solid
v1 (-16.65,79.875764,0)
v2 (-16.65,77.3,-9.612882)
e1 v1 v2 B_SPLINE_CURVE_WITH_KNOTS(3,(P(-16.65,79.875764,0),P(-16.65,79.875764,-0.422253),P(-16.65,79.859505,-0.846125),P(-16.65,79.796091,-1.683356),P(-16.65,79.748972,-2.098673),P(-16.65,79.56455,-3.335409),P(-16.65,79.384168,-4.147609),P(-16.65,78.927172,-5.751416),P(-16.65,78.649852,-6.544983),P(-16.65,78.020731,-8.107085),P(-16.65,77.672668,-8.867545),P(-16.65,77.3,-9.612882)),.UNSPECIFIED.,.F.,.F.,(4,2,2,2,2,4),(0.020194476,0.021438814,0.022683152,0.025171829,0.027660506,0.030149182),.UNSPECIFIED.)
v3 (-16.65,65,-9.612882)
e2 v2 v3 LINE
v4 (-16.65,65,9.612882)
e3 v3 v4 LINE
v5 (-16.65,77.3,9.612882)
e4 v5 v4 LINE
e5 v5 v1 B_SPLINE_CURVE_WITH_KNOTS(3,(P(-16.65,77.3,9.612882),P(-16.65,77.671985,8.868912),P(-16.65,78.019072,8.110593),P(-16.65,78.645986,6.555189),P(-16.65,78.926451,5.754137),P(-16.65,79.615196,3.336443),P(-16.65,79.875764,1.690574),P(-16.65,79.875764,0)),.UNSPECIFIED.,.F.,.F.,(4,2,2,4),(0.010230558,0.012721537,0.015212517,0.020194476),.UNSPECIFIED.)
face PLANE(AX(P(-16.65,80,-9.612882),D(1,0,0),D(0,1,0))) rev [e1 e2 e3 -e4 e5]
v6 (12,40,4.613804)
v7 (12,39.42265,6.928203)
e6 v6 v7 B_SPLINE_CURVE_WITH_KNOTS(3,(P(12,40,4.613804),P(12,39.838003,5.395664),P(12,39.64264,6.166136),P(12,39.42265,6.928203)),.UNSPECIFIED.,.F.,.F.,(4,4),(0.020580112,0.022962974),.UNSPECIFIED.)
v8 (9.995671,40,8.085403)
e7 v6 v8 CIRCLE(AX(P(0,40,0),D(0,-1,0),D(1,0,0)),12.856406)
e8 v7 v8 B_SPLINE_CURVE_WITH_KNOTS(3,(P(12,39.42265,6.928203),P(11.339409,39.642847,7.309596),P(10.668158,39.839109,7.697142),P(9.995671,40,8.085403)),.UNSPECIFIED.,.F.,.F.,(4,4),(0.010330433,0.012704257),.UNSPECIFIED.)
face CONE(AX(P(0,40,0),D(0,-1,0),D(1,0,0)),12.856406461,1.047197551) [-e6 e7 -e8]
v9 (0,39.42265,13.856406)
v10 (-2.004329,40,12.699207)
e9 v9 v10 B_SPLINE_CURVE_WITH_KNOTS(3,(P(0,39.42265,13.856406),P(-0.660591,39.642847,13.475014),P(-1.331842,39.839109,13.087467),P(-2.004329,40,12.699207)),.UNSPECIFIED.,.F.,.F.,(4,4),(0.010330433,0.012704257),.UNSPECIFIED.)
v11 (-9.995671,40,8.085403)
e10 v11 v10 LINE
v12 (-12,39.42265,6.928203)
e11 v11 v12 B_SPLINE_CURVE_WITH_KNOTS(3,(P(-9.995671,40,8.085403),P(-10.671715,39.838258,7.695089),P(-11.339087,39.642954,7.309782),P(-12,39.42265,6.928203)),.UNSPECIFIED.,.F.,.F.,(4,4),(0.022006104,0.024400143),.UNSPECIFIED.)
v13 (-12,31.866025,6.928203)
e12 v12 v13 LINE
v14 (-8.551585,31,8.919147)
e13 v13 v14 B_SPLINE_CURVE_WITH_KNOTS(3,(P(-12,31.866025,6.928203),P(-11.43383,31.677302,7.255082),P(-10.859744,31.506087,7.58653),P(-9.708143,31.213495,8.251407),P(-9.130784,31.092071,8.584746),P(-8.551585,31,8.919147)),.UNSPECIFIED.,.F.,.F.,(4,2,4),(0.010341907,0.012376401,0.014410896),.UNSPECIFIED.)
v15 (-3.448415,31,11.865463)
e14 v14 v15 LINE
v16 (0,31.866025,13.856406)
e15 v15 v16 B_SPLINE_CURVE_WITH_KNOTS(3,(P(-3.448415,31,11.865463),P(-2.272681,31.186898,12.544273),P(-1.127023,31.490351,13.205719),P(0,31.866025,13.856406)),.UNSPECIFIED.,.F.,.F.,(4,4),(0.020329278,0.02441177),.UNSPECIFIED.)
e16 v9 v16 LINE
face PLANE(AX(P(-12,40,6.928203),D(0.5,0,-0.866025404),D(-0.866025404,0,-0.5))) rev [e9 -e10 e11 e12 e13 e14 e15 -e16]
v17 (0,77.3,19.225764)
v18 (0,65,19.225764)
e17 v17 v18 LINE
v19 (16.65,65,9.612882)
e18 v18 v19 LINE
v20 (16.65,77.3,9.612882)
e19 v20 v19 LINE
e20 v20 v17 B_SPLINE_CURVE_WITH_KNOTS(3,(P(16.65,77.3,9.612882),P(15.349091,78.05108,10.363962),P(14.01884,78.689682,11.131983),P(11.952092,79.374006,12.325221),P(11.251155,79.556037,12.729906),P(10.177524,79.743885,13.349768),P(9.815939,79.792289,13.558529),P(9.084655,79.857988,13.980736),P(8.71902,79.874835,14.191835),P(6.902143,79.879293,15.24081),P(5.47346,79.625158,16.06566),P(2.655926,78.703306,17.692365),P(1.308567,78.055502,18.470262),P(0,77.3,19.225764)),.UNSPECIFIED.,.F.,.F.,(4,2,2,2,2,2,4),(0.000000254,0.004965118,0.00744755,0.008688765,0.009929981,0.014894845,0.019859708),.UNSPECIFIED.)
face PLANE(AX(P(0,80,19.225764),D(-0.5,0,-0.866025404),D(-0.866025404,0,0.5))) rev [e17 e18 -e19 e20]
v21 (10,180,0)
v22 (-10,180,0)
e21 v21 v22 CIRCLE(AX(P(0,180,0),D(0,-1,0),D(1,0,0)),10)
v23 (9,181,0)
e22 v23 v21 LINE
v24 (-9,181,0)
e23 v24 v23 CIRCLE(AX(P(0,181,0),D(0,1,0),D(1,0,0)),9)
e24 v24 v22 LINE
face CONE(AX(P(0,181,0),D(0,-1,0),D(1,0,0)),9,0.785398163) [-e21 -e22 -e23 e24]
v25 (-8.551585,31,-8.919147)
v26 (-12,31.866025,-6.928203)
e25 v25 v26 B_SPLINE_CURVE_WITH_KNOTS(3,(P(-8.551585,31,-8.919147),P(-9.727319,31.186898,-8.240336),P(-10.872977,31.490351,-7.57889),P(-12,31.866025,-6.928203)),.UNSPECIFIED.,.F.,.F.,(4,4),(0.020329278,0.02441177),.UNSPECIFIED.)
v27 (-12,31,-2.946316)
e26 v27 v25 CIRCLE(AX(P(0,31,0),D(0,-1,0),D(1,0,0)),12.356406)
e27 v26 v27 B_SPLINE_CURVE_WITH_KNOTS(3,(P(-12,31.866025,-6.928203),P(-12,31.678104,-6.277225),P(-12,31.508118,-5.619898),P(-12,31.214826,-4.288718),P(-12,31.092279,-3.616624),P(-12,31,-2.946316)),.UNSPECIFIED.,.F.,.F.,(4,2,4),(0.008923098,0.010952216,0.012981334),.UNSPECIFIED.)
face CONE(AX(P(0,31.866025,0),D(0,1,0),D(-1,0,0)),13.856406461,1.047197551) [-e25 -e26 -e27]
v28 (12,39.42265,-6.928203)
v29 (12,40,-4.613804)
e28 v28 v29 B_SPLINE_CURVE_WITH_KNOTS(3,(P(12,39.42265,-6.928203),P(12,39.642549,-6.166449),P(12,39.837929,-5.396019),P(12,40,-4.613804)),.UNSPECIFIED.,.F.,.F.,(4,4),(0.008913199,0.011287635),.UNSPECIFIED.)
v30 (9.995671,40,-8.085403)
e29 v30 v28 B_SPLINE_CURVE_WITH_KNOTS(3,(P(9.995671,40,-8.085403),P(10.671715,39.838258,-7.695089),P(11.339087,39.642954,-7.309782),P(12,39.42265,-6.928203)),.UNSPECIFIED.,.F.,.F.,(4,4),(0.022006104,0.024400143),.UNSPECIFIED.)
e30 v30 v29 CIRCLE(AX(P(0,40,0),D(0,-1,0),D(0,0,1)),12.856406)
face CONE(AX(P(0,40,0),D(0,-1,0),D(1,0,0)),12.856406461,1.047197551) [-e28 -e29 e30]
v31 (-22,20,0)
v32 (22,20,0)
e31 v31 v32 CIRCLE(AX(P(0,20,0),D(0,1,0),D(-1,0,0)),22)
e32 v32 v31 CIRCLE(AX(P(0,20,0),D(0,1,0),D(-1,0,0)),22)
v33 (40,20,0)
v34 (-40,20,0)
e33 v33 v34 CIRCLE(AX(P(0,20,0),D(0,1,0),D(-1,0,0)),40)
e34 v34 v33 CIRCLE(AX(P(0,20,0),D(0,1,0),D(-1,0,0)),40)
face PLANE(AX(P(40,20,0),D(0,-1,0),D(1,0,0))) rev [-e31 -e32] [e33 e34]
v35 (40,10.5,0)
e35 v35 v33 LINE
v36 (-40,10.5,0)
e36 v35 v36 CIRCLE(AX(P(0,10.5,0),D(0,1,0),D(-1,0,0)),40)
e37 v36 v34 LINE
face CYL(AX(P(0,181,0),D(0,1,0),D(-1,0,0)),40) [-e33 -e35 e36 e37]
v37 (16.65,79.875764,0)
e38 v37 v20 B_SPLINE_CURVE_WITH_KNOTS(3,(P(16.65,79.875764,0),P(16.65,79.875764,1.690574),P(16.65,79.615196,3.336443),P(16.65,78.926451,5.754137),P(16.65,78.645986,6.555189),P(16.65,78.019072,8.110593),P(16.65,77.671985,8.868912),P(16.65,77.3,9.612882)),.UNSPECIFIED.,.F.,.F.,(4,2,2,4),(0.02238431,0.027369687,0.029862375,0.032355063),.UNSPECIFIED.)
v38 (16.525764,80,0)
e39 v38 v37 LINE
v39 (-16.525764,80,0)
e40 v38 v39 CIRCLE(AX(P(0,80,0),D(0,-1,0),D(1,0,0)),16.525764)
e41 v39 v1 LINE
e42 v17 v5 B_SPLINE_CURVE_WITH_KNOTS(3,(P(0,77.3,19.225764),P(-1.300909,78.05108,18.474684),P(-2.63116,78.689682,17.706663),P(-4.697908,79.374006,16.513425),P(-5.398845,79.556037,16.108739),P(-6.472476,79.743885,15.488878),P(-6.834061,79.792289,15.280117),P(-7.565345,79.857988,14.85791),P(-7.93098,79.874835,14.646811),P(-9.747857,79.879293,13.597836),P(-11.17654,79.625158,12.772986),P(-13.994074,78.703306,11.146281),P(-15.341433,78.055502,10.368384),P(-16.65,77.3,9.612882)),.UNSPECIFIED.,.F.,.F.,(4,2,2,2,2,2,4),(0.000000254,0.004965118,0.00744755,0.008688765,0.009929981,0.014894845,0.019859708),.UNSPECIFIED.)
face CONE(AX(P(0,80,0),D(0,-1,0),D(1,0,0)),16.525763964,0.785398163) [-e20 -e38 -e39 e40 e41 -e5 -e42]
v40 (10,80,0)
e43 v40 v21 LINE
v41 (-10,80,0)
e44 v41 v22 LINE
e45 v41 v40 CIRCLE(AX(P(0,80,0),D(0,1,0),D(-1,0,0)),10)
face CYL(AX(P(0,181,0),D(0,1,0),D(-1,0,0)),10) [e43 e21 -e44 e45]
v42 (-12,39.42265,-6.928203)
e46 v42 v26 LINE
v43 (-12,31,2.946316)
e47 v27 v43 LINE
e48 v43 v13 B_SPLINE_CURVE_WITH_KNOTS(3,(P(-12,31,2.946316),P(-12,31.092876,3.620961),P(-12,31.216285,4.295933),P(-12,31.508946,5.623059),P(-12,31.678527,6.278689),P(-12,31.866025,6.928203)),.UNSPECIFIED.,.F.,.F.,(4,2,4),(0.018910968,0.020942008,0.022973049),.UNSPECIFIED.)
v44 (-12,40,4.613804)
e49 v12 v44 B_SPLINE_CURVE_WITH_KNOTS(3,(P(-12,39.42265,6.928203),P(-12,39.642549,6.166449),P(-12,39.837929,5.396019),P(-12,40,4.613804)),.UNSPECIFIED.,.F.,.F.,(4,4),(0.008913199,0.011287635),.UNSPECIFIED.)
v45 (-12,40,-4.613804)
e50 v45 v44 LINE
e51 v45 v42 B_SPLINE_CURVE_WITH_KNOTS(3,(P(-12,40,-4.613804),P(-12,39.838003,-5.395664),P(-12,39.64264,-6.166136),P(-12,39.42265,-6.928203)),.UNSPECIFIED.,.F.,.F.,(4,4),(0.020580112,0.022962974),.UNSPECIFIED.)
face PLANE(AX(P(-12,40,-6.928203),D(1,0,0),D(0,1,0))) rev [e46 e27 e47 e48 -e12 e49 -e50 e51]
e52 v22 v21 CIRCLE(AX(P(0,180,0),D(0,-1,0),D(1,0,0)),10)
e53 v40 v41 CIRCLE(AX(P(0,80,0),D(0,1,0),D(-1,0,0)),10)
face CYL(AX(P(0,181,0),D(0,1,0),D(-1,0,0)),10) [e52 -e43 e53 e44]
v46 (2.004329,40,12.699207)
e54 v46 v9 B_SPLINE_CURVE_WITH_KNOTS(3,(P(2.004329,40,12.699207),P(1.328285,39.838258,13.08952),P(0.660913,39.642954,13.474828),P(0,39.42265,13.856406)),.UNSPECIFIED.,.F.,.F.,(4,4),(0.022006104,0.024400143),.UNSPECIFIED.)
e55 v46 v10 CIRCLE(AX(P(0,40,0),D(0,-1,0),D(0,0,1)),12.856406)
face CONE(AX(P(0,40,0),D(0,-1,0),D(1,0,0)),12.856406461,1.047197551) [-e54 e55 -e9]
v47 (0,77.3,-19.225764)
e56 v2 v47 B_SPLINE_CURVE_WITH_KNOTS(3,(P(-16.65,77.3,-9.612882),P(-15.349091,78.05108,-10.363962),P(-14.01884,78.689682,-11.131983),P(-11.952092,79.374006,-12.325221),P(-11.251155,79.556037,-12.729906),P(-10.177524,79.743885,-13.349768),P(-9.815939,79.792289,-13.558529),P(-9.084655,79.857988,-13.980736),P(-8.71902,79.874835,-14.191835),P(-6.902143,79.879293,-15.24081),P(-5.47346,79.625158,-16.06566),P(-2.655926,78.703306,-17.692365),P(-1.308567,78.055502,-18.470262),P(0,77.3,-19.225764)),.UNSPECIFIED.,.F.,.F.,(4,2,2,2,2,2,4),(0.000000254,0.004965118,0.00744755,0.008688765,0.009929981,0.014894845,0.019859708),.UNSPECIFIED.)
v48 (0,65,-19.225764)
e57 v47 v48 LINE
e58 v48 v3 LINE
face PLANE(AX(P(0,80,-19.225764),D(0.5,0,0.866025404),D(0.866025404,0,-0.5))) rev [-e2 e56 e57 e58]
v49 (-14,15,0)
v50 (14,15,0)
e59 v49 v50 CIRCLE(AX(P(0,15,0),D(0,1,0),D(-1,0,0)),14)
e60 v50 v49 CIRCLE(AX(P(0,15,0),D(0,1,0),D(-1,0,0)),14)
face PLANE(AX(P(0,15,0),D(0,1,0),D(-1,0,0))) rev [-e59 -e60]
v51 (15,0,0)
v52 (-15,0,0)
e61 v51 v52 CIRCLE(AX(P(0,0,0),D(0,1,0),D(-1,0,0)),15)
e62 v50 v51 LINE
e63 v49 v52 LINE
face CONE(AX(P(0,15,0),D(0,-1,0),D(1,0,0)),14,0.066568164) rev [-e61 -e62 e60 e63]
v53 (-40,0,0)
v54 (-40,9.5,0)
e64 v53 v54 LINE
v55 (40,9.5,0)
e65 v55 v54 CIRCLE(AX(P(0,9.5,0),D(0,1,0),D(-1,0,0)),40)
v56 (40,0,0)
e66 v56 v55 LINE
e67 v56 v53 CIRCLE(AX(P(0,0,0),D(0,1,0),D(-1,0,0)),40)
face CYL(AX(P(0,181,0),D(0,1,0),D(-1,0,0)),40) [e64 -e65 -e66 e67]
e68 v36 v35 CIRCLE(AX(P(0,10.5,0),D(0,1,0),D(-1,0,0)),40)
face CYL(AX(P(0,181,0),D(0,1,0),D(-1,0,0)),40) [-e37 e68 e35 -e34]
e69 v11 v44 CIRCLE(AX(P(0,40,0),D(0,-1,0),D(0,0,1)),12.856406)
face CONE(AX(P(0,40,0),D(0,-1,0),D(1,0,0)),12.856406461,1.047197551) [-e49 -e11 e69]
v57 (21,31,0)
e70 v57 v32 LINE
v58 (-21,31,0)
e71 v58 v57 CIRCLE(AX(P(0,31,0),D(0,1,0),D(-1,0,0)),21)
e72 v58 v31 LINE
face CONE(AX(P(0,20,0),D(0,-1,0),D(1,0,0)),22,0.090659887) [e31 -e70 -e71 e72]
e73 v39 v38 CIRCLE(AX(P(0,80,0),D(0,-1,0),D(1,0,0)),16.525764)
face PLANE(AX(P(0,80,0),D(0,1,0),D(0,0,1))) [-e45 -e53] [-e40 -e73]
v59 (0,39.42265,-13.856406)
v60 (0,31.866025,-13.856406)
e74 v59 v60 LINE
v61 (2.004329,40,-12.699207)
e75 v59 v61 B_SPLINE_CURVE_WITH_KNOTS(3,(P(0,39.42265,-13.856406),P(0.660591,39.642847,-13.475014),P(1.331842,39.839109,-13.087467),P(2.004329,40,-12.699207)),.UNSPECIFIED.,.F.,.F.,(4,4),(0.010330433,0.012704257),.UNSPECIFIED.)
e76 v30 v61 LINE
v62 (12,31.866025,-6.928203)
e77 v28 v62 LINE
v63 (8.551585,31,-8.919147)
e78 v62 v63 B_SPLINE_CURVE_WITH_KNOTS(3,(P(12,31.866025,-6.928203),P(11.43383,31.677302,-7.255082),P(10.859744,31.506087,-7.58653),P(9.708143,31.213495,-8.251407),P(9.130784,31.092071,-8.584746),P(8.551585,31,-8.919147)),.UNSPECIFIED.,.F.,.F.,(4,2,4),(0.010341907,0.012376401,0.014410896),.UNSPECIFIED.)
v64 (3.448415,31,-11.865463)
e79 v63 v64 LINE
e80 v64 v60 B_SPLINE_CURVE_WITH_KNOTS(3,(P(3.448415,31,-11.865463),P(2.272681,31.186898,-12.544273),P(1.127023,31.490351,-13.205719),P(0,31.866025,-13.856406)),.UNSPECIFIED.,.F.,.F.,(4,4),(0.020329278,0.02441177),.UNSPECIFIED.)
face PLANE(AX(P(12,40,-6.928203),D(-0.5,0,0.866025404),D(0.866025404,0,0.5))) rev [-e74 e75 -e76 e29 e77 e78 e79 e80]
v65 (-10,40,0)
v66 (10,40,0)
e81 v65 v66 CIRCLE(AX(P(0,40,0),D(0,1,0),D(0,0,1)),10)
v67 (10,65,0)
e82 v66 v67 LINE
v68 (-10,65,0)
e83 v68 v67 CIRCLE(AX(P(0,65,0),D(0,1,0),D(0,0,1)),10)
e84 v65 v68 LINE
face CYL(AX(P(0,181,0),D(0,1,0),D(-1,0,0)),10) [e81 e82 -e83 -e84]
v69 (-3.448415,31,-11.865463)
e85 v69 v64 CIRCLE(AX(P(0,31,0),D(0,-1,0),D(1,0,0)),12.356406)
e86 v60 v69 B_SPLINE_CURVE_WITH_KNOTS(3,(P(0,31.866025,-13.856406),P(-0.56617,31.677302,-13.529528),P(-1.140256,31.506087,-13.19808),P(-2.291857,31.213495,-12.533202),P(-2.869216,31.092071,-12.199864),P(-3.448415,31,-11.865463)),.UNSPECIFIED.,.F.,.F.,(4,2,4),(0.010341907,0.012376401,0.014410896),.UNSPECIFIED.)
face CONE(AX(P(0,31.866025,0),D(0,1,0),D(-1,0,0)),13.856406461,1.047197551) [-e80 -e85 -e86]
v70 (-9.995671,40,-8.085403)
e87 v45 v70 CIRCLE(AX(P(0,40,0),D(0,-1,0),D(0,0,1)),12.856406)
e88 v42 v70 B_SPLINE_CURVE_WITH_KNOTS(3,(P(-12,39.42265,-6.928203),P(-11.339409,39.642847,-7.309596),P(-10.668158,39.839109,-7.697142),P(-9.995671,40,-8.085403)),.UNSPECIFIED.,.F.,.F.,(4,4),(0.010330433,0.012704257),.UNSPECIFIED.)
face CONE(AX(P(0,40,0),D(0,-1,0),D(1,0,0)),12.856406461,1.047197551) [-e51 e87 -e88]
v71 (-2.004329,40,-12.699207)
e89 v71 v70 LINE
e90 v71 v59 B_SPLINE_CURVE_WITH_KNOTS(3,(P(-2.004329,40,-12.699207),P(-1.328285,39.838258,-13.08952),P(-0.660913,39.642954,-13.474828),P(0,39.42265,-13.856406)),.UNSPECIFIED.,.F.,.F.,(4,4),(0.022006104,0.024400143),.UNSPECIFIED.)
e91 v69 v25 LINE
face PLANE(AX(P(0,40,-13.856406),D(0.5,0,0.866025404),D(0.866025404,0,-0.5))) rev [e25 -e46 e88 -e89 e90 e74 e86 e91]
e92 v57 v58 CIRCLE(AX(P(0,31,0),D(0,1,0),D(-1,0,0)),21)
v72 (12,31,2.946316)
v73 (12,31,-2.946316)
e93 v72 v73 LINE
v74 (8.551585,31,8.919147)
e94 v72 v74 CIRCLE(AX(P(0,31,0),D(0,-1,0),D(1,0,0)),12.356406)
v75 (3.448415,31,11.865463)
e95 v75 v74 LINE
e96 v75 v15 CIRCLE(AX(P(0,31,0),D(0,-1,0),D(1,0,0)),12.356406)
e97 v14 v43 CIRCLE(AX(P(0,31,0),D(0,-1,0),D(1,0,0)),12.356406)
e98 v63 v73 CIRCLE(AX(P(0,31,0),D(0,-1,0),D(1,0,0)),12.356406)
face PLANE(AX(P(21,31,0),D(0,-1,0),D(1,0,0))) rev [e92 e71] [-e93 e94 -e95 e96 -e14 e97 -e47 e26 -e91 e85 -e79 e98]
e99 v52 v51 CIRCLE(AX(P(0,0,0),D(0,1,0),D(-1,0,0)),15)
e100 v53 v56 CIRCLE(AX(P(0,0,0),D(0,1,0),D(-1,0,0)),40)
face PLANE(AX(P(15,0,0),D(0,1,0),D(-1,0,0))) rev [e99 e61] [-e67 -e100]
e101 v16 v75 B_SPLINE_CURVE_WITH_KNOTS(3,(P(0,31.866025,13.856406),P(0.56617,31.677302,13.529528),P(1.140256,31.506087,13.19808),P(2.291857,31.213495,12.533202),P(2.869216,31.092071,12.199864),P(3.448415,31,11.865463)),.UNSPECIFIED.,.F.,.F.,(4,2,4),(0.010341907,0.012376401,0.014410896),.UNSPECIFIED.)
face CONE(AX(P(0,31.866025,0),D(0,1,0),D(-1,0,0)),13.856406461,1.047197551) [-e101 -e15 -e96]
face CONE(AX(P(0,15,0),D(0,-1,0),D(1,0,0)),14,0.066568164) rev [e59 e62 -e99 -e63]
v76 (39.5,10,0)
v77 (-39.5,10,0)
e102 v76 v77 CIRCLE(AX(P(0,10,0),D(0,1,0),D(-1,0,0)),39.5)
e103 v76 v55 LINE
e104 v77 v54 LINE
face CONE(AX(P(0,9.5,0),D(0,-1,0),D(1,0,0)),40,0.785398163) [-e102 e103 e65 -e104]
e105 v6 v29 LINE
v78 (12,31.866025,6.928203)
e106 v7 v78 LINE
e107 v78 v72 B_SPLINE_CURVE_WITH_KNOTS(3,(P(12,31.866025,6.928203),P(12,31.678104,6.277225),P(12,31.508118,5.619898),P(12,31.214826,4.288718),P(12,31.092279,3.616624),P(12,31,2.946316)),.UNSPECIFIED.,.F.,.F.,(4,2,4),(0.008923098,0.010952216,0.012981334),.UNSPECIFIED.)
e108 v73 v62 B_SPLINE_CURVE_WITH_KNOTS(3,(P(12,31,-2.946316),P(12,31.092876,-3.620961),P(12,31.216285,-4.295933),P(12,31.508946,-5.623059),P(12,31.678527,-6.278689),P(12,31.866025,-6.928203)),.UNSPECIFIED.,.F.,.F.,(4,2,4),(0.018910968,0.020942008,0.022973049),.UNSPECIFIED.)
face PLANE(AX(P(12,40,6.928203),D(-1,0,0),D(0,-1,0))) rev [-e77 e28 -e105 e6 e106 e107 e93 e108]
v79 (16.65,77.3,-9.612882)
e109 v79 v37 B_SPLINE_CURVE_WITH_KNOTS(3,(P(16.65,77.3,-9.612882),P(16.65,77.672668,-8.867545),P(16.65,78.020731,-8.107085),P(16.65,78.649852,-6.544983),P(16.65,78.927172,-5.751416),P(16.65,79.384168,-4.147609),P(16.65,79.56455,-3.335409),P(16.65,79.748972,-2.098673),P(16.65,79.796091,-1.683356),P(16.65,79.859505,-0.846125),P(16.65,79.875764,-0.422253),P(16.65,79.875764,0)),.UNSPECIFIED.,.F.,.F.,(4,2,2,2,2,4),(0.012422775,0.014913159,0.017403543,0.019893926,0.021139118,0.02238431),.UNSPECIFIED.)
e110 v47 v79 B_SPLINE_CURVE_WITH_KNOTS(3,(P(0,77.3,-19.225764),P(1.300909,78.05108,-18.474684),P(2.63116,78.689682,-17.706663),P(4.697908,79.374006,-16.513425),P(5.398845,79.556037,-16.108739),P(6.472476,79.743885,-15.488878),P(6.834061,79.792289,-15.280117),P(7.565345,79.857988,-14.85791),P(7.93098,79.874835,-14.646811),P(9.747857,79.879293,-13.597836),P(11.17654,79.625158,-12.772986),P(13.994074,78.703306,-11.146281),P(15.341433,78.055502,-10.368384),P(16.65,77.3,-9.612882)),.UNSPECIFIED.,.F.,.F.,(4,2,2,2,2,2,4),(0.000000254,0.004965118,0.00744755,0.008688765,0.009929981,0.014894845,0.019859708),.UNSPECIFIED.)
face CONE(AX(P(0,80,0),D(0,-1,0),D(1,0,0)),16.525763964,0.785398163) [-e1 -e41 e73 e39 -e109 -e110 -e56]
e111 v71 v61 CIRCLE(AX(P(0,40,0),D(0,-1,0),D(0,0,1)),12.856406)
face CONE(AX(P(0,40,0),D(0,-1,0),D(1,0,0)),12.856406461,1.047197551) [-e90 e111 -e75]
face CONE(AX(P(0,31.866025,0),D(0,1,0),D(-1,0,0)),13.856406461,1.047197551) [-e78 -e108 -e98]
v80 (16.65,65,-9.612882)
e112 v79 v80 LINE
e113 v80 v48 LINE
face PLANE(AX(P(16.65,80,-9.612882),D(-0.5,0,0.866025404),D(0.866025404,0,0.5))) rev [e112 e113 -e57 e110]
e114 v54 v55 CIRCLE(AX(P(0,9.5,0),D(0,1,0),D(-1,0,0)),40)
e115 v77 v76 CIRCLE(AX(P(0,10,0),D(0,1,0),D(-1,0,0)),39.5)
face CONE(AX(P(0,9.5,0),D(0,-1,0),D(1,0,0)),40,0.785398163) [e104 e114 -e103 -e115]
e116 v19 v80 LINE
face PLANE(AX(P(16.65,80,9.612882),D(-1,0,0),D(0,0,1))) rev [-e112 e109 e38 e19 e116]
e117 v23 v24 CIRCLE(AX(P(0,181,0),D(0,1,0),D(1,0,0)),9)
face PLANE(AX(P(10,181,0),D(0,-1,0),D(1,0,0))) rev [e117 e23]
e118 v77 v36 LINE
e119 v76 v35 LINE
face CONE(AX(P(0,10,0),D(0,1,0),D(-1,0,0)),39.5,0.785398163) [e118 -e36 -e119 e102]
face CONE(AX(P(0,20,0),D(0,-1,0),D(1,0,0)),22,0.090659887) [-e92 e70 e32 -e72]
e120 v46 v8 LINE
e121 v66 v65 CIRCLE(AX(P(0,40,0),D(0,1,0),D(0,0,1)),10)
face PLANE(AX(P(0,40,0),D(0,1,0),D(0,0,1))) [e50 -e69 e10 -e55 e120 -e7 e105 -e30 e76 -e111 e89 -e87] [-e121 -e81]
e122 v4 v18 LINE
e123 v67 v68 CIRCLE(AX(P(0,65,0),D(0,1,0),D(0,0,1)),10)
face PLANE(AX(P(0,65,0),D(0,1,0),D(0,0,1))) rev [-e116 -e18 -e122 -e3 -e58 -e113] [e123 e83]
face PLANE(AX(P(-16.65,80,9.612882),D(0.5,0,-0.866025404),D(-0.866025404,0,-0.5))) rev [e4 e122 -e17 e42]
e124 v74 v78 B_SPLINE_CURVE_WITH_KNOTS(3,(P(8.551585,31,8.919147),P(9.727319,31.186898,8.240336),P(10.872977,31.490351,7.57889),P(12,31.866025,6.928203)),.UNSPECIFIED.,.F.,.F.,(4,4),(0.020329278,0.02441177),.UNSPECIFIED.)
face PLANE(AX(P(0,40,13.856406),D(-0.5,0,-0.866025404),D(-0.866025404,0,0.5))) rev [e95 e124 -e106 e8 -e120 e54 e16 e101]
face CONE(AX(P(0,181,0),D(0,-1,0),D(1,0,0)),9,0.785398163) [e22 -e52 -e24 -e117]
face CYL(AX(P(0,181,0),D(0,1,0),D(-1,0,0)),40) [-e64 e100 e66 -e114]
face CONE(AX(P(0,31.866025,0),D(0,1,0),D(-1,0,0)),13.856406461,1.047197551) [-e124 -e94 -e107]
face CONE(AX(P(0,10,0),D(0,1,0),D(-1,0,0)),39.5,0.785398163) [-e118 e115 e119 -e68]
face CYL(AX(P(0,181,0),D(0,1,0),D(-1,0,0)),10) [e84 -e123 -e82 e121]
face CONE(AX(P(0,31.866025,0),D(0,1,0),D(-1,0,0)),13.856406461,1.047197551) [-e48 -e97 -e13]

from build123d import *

# Parameters (mm, degrees)
BOSS_EXTRUDE1_DEPTH = 9
BOSS_EXTRUDE2_START = 39
SKETCH5_R           = 10
BOSS_EXTRUDE2_DEPTH = 15
CHAMFER1_SIZE       = 1


with BuildPart() as part:
    # Sketch1 → Revolve1 (revolve)
    with BuildSketch(Plane.XY, mode=Mode.PRIVATE) as revolve1_sk:
        Polygon((15, 0), (40, 0), (40, 9.5), (39.5, 10), (40, 10.5), (40, 20), (22, 20), (21, 31), (10, 31), (10, 181), (0, 181), (0, 15), (14, 15), align=None)
    revolve(revolve1_sk.sketch.rotate(Axis((0, 181, 0), (0, -1, 0)), 180), axis=Axis((0, 181, 0), (0, -1, 0)))

    # Sketch2 → Boss-Extrude1 (add)
    with BuildSketch(Plane(origin=(0, 31, 0), x_dir=(1, 0, 0), z_dir=(0, 1, 0))):
        Polygon((12, 6.92820323), (0, 13.856406461), (-12, 6.92820323), (-12, -6.92820323), (0, -13.856406461), (12, -6.92820323), align=None)
    extrude(amount=BOSS_EXTRUDE1_DEPTH)

    # Sketch3 → Cut-Revolve1 (revolve, cut)
    with BuildSketch(Plane(origin=(0, 0, 0), x_dir=(0, 0, -1), z_dir=(1, 0, 0))):
        Polygon((12.356406461, 31), (13.856406461, 31.866025404), (13.856406461, 31), align=None)
        Polygon((13.856406461, 39.422649731), (12.856406461, 40), (13.856406461, 40), align=None)
    revolve(axis=Axis((0, 181, 0), (0, 1, 0)), mode=Mode.SUBTRACT)

    # Sketch5 → Boss-Extrude2 (add)
    with BuildSketch(Plane(origin=(0, 41, 0), x_dir=(-1, 0, 0), z_dir=(0, 1, 0)).offset(BOSS_EXTRUDE2_START)):
        Polygon((0, 19.225763964), (-16.65, 9.612881982), (-16.65, -9.612881982), (0, -19.225763964), (16.65, -9.612881982), (16.65, 9.612881982), align=None)
        with Locations(Location((0, 0, 0), (0, 0, 90))):
            Circle(SKETCH5_R, mode=Mode.SUBTRACT)
    extrude(amount=-BOSS_EXTRUDE2_DEPTH)

    # Sketch7 → Cut-Revolve3 (revolve, cut)
    with BuildSketch(Plane(origin=(0, 0, 0), x_dir=(0, 0, -1), z_dir=(1, 0, 0)), mode=Mode.PRIVATE) as cut_revolve3_sk:
        Polygon((16.525763964, 80), (19.225763964, 77.3), (19.225763964, 80), align=None)
        Polygon((16.525763964, 41), (19.225763964, 43.7), (19.225763964, 41), align=None)
    revolve(cut_revolve3_sk.sketch.rotate(Axis((0, 181, 0), (0, 1, 0)), 180), axis=Axis((0, 181, 0), (0, 1, 0)), mode=Mode.SUBTRACT)

    # Chamfer1
    chamfer1_edges = [part.edges().sort_by_distance(p)[0] for p in [
        (10, 181, 0),
    ]]
    chamfer(chamfer1_edges, length=CHAMFER1_SIZE)


solid = part.part
